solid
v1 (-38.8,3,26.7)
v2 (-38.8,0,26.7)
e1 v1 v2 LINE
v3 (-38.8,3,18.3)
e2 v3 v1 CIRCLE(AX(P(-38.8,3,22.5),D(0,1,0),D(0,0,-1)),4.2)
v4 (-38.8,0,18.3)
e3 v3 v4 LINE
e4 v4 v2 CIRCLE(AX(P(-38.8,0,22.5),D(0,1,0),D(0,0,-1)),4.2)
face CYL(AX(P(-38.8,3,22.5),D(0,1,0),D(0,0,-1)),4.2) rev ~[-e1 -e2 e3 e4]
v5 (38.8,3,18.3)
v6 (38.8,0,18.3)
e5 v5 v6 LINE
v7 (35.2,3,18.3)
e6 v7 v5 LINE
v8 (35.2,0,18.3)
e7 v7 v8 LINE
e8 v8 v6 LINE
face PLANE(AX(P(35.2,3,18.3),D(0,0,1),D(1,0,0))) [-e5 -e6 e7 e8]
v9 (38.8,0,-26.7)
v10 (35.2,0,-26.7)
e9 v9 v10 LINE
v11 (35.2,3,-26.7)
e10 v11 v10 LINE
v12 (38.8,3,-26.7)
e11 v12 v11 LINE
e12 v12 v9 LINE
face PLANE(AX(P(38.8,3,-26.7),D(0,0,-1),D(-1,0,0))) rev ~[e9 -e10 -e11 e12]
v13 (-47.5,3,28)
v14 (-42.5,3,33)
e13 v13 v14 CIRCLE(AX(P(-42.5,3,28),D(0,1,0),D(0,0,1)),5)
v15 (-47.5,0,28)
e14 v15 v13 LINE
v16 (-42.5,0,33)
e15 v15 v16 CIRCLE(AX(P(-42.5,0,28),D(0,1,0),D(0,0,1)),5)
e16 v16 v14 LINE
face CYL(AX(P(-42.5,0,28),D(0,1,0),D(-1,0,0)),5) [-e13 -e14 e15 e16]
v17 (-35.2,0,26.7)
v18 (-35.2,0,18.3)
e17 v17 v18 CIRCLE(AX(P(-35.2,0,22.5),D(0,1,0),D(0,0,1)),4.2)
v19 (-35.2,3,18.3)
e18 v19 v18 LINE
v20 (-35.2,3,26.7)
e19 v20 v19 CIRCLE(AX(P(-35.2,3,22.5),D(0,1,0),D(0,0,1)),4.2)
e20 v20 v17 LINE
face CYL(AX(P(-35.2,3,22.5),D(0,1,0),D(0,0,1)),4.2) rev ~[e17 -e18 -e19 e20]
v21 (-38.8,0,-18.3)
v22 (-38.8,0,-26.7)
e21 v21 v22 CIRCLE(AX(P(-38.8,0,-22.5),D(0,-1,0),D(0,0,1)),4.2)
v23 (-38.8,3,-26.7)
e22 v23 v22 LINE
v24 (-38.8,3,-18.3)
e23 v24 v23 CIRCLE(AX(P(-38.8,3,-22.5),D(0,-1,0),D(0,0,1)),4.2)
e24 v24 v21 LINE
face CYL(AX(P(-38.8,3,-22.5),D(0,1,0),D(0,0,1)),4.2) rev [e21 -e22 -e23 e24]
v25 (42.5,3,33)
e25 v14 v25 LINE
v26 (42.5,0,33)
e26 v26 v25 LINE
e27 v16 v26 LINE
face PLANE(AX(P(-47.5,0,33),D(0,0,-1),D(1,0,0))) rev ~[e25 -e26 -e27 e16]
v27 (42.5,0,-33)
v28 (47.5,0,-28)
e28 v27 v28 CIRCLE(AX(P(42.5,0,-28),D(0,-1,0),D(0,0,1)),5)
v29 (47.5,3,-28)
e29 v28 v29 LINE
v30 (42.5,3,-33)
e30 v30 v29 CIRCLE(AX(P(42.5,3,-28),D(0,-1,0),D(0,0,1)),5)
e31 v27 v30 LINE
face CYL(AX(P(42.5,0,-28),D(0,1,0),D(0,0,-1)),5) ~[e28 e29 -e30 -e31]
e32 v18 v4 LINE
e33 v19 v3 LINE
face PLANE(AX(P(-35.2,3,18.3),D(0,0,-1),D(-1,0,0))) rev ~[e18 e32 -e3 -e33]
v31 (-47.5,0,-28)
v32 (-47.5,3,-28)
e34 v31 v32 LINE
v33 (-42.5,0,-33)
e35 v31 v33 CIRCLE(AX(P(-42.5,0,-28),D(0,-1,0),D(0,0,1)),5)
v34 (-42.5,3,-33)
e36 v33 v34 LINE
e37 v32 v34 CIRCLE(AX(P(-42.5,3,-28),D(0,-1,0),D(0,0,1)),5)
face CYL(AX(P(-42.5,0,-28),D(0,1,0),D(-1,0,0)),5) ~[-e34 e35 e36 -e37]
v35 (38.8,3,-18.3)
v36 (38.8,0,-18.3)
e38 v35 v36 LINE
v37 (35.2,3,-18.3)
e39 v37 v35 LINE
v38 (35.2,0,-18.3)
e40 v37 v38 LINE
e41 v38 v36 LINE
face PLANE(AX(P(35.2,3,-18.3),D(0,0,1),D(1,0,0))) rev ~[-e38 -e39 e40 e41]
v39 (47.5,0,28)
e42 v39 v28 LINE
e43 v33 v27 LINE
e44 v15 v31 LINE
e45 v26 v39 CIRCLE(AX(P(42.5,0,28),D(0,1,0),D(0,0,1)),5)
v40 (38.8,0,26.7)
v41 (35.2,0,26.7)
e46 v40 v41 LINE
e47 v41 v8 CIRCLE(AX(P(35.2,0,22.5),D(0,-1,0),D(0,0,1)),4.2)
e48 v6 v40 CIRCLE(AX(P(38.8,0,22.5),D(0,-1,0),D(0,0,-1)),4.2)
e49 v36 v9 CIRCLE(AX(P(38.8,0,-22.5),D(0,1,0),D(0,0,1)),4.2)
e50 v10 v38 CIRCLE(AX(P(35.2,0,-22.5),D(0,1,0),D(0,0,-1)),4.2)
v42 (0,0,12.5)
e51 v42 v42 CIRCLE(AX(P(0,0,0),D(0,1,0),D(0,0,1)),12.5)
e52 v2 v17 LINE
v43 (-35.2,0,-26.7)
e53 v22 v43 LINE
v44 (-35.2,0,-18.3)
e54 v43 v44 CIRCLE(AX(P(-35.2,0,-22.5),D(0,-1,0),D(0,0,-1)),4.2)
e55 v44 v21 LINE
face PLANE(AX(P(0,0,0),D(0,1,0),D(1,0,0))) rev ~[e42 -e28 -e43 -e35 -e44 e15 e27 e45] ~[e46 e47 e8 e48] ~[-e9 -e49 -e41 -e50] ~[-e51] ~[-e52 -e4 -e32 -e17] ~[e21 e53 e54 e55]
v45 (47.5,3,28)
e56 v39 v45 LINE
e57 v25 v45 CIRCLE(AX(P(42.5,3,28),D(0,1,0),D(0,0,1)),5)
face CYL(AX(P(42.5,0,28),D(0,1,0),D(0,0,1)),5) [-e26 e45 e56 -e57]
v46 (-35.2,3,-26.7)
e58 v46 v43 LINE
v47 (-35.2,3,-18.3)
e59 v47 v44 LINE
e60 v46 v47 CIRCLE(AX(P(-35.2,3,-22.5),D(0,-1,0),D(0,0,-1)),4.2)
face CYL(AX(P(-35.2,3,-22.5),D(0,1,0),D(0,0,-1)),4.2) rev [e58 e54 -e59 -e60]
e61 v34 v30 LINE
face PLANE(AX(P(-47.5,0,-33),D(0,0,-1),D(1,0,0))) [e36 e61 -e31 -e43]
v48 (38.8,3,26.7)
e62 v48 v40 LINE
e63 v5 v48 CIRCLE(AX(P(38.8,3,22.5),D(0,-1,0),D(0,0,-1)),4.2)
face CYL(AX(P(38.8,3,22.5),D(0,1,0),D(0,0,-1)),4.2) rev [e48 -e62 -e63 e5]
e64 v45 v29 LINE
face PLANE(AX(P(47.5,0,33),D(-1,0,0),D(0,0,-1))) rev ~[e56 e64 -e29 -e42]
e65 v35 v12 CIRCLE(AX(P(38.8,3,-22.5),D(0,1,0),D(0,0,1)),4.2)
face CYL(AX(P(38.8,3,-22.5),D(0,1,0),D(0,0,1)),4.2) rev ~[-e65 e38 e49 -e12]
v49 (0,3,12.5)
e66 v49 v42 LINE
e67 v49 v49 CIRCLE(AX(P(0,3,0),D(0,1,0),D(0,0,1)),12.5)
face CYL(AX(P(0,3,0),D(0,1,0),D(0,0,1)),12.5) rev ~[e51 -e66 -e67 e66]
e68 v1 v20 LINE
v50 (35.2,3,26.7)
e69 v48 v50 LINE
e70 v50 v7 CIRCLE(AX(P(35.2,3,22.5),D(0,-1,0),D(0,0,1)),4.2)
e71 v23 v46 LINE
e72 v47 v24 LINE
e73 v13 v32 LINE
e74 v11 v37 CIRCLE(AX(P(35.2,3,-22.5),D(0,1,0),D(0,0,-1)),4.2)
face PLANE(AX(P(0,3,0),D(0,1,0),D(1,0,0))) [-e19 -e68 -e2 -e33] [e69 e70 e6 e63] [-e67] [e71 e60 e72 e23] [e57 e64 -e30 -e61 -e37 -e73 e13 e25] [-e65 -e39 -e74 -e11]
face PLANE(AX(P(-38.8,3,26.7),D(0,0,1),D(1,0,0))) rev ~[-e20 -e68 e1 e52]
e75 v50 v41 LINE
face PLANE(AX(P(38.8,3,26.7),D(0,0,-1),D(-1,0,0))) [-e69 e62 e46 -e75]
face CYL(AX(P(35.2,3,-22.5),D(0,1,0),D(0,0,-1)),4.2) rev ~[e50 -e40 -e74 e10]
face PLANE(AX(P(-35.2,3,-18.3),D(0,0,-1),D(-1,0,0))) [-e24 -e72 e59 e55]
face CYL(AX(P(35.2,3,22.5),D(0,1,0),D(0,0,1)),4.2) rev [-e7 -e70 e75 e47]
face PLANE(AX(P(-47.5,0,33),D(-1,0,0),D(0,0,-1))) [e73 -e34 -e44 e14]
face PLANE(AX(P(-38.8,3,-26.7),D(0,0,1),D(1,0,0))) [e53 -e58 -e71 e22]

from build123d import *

# Parameters (mm, degrees)
SKETCH_1_W          = 95
SKETCH_1_H          = 66
EXTRUDE_1_DEPTH     = 3
CUT_EXTRUDE_1_DEPTH = 3
FILLET_1_R          = 5
SKETCH_3_R          = 12.5
CUT_EXTRUDE_2_DEPTH = 3


with BuildPart() as part:
    # 草图1 → 凸台-拉伸1 (new body)
    with BuildSketch(Plane(origin=(0, 0, 0), x_dir=(1, 0, 0), z_dir=(0, 1, 0))):
        Rectangle(SKETCH_1_W, SKETCH_1_H)
    extrude(amount=EXTRUDE_1_DEPTH)

    # 草图2 → 切除-拉伸1 (cut)
    with BuildSketch(Plane(origin=(0, 3, 0), x_dir=(1, 0, 0), z_dir=(0, 1, 0))):
        with BuildLine():
            Line((-38.8, 26.7), (-35.2, 26.7))
            ThreePointArc((-35.2, 26.7), (-31, 22.5), (-35.2, 18.3))
            Line((-35.2, 18.3), (-38.8, 18.3))
            ThreePointArc((-38.8, 18.3), (-43, 22.5), (-38.8, 26.7))
        make_face()
        with BuildLine():
            Line((-38.8, -26.7), (-35.2, -26.7))
            ThreePointArc((-35.2, -26.7), (-31, -22.5), (-35.2, -18.3))
            Line((-35.2, -18.3), (-38.8, -18.3))
            ThreePointArc((-38.8, -18.3), (-43, -22.5), (-38.8, -26.7))
        make_face()
        with BuildLine():
            Line((38.8, 26.7), (35.2, 26.7))
            ThreePointArc((35.2, 26.7), (31, 22.5), (35.2, 18.3))
            Line((35.2, 18.3), (38.8, 18.3))
            ThreePointArc((38.8, 18.3), (43, 22.5), (38.8, 26.7))
        make_face()
        with BuildLine():
            Line((38.8, -26.7), (35.2, -26.7))
            ThreePointArc((35.2, -26.7), (31, -22.5), (35.2, -18.3))
            Line((35.2, -18.3), (38.8, -18.3))
            ThreePointArc((38.8, -18.3), (43, -22.5), (38.8, -26.7))
        make_face()
    extrude(amount=-CUT_EXTRUDE_1_DEPTH, mode=Mode.SUBTRACT)

    # 圆角1
    fillet_1_edges = [part.edges().sort_by_distance(p)[0] for p in [
        (47.5, 1.5, 33),
        (-47.5, 1.5, 33),
        (-47.5, 1.5, -33),
        (47.5, 1.5, -33),
    ]]
    fillet(fillet_1_edges, radius=FILLET_1_R)

    # 草图3 → 切除-拉伸2 (cut)
    with BuildSketch(Plane(origin=(0, 3, 0), x_dir=(1, 0, 0), z_dir=(0, 1, 0))):
        with Locations(Location((0, 0, 0), (0, 0, 270))):
            Circle(SKETCH_3_R)
    extrude(amount=-CUT_EXTRUDE_2_DEPTH, mode=Mode.SUBTRACT)


solid = part.part
